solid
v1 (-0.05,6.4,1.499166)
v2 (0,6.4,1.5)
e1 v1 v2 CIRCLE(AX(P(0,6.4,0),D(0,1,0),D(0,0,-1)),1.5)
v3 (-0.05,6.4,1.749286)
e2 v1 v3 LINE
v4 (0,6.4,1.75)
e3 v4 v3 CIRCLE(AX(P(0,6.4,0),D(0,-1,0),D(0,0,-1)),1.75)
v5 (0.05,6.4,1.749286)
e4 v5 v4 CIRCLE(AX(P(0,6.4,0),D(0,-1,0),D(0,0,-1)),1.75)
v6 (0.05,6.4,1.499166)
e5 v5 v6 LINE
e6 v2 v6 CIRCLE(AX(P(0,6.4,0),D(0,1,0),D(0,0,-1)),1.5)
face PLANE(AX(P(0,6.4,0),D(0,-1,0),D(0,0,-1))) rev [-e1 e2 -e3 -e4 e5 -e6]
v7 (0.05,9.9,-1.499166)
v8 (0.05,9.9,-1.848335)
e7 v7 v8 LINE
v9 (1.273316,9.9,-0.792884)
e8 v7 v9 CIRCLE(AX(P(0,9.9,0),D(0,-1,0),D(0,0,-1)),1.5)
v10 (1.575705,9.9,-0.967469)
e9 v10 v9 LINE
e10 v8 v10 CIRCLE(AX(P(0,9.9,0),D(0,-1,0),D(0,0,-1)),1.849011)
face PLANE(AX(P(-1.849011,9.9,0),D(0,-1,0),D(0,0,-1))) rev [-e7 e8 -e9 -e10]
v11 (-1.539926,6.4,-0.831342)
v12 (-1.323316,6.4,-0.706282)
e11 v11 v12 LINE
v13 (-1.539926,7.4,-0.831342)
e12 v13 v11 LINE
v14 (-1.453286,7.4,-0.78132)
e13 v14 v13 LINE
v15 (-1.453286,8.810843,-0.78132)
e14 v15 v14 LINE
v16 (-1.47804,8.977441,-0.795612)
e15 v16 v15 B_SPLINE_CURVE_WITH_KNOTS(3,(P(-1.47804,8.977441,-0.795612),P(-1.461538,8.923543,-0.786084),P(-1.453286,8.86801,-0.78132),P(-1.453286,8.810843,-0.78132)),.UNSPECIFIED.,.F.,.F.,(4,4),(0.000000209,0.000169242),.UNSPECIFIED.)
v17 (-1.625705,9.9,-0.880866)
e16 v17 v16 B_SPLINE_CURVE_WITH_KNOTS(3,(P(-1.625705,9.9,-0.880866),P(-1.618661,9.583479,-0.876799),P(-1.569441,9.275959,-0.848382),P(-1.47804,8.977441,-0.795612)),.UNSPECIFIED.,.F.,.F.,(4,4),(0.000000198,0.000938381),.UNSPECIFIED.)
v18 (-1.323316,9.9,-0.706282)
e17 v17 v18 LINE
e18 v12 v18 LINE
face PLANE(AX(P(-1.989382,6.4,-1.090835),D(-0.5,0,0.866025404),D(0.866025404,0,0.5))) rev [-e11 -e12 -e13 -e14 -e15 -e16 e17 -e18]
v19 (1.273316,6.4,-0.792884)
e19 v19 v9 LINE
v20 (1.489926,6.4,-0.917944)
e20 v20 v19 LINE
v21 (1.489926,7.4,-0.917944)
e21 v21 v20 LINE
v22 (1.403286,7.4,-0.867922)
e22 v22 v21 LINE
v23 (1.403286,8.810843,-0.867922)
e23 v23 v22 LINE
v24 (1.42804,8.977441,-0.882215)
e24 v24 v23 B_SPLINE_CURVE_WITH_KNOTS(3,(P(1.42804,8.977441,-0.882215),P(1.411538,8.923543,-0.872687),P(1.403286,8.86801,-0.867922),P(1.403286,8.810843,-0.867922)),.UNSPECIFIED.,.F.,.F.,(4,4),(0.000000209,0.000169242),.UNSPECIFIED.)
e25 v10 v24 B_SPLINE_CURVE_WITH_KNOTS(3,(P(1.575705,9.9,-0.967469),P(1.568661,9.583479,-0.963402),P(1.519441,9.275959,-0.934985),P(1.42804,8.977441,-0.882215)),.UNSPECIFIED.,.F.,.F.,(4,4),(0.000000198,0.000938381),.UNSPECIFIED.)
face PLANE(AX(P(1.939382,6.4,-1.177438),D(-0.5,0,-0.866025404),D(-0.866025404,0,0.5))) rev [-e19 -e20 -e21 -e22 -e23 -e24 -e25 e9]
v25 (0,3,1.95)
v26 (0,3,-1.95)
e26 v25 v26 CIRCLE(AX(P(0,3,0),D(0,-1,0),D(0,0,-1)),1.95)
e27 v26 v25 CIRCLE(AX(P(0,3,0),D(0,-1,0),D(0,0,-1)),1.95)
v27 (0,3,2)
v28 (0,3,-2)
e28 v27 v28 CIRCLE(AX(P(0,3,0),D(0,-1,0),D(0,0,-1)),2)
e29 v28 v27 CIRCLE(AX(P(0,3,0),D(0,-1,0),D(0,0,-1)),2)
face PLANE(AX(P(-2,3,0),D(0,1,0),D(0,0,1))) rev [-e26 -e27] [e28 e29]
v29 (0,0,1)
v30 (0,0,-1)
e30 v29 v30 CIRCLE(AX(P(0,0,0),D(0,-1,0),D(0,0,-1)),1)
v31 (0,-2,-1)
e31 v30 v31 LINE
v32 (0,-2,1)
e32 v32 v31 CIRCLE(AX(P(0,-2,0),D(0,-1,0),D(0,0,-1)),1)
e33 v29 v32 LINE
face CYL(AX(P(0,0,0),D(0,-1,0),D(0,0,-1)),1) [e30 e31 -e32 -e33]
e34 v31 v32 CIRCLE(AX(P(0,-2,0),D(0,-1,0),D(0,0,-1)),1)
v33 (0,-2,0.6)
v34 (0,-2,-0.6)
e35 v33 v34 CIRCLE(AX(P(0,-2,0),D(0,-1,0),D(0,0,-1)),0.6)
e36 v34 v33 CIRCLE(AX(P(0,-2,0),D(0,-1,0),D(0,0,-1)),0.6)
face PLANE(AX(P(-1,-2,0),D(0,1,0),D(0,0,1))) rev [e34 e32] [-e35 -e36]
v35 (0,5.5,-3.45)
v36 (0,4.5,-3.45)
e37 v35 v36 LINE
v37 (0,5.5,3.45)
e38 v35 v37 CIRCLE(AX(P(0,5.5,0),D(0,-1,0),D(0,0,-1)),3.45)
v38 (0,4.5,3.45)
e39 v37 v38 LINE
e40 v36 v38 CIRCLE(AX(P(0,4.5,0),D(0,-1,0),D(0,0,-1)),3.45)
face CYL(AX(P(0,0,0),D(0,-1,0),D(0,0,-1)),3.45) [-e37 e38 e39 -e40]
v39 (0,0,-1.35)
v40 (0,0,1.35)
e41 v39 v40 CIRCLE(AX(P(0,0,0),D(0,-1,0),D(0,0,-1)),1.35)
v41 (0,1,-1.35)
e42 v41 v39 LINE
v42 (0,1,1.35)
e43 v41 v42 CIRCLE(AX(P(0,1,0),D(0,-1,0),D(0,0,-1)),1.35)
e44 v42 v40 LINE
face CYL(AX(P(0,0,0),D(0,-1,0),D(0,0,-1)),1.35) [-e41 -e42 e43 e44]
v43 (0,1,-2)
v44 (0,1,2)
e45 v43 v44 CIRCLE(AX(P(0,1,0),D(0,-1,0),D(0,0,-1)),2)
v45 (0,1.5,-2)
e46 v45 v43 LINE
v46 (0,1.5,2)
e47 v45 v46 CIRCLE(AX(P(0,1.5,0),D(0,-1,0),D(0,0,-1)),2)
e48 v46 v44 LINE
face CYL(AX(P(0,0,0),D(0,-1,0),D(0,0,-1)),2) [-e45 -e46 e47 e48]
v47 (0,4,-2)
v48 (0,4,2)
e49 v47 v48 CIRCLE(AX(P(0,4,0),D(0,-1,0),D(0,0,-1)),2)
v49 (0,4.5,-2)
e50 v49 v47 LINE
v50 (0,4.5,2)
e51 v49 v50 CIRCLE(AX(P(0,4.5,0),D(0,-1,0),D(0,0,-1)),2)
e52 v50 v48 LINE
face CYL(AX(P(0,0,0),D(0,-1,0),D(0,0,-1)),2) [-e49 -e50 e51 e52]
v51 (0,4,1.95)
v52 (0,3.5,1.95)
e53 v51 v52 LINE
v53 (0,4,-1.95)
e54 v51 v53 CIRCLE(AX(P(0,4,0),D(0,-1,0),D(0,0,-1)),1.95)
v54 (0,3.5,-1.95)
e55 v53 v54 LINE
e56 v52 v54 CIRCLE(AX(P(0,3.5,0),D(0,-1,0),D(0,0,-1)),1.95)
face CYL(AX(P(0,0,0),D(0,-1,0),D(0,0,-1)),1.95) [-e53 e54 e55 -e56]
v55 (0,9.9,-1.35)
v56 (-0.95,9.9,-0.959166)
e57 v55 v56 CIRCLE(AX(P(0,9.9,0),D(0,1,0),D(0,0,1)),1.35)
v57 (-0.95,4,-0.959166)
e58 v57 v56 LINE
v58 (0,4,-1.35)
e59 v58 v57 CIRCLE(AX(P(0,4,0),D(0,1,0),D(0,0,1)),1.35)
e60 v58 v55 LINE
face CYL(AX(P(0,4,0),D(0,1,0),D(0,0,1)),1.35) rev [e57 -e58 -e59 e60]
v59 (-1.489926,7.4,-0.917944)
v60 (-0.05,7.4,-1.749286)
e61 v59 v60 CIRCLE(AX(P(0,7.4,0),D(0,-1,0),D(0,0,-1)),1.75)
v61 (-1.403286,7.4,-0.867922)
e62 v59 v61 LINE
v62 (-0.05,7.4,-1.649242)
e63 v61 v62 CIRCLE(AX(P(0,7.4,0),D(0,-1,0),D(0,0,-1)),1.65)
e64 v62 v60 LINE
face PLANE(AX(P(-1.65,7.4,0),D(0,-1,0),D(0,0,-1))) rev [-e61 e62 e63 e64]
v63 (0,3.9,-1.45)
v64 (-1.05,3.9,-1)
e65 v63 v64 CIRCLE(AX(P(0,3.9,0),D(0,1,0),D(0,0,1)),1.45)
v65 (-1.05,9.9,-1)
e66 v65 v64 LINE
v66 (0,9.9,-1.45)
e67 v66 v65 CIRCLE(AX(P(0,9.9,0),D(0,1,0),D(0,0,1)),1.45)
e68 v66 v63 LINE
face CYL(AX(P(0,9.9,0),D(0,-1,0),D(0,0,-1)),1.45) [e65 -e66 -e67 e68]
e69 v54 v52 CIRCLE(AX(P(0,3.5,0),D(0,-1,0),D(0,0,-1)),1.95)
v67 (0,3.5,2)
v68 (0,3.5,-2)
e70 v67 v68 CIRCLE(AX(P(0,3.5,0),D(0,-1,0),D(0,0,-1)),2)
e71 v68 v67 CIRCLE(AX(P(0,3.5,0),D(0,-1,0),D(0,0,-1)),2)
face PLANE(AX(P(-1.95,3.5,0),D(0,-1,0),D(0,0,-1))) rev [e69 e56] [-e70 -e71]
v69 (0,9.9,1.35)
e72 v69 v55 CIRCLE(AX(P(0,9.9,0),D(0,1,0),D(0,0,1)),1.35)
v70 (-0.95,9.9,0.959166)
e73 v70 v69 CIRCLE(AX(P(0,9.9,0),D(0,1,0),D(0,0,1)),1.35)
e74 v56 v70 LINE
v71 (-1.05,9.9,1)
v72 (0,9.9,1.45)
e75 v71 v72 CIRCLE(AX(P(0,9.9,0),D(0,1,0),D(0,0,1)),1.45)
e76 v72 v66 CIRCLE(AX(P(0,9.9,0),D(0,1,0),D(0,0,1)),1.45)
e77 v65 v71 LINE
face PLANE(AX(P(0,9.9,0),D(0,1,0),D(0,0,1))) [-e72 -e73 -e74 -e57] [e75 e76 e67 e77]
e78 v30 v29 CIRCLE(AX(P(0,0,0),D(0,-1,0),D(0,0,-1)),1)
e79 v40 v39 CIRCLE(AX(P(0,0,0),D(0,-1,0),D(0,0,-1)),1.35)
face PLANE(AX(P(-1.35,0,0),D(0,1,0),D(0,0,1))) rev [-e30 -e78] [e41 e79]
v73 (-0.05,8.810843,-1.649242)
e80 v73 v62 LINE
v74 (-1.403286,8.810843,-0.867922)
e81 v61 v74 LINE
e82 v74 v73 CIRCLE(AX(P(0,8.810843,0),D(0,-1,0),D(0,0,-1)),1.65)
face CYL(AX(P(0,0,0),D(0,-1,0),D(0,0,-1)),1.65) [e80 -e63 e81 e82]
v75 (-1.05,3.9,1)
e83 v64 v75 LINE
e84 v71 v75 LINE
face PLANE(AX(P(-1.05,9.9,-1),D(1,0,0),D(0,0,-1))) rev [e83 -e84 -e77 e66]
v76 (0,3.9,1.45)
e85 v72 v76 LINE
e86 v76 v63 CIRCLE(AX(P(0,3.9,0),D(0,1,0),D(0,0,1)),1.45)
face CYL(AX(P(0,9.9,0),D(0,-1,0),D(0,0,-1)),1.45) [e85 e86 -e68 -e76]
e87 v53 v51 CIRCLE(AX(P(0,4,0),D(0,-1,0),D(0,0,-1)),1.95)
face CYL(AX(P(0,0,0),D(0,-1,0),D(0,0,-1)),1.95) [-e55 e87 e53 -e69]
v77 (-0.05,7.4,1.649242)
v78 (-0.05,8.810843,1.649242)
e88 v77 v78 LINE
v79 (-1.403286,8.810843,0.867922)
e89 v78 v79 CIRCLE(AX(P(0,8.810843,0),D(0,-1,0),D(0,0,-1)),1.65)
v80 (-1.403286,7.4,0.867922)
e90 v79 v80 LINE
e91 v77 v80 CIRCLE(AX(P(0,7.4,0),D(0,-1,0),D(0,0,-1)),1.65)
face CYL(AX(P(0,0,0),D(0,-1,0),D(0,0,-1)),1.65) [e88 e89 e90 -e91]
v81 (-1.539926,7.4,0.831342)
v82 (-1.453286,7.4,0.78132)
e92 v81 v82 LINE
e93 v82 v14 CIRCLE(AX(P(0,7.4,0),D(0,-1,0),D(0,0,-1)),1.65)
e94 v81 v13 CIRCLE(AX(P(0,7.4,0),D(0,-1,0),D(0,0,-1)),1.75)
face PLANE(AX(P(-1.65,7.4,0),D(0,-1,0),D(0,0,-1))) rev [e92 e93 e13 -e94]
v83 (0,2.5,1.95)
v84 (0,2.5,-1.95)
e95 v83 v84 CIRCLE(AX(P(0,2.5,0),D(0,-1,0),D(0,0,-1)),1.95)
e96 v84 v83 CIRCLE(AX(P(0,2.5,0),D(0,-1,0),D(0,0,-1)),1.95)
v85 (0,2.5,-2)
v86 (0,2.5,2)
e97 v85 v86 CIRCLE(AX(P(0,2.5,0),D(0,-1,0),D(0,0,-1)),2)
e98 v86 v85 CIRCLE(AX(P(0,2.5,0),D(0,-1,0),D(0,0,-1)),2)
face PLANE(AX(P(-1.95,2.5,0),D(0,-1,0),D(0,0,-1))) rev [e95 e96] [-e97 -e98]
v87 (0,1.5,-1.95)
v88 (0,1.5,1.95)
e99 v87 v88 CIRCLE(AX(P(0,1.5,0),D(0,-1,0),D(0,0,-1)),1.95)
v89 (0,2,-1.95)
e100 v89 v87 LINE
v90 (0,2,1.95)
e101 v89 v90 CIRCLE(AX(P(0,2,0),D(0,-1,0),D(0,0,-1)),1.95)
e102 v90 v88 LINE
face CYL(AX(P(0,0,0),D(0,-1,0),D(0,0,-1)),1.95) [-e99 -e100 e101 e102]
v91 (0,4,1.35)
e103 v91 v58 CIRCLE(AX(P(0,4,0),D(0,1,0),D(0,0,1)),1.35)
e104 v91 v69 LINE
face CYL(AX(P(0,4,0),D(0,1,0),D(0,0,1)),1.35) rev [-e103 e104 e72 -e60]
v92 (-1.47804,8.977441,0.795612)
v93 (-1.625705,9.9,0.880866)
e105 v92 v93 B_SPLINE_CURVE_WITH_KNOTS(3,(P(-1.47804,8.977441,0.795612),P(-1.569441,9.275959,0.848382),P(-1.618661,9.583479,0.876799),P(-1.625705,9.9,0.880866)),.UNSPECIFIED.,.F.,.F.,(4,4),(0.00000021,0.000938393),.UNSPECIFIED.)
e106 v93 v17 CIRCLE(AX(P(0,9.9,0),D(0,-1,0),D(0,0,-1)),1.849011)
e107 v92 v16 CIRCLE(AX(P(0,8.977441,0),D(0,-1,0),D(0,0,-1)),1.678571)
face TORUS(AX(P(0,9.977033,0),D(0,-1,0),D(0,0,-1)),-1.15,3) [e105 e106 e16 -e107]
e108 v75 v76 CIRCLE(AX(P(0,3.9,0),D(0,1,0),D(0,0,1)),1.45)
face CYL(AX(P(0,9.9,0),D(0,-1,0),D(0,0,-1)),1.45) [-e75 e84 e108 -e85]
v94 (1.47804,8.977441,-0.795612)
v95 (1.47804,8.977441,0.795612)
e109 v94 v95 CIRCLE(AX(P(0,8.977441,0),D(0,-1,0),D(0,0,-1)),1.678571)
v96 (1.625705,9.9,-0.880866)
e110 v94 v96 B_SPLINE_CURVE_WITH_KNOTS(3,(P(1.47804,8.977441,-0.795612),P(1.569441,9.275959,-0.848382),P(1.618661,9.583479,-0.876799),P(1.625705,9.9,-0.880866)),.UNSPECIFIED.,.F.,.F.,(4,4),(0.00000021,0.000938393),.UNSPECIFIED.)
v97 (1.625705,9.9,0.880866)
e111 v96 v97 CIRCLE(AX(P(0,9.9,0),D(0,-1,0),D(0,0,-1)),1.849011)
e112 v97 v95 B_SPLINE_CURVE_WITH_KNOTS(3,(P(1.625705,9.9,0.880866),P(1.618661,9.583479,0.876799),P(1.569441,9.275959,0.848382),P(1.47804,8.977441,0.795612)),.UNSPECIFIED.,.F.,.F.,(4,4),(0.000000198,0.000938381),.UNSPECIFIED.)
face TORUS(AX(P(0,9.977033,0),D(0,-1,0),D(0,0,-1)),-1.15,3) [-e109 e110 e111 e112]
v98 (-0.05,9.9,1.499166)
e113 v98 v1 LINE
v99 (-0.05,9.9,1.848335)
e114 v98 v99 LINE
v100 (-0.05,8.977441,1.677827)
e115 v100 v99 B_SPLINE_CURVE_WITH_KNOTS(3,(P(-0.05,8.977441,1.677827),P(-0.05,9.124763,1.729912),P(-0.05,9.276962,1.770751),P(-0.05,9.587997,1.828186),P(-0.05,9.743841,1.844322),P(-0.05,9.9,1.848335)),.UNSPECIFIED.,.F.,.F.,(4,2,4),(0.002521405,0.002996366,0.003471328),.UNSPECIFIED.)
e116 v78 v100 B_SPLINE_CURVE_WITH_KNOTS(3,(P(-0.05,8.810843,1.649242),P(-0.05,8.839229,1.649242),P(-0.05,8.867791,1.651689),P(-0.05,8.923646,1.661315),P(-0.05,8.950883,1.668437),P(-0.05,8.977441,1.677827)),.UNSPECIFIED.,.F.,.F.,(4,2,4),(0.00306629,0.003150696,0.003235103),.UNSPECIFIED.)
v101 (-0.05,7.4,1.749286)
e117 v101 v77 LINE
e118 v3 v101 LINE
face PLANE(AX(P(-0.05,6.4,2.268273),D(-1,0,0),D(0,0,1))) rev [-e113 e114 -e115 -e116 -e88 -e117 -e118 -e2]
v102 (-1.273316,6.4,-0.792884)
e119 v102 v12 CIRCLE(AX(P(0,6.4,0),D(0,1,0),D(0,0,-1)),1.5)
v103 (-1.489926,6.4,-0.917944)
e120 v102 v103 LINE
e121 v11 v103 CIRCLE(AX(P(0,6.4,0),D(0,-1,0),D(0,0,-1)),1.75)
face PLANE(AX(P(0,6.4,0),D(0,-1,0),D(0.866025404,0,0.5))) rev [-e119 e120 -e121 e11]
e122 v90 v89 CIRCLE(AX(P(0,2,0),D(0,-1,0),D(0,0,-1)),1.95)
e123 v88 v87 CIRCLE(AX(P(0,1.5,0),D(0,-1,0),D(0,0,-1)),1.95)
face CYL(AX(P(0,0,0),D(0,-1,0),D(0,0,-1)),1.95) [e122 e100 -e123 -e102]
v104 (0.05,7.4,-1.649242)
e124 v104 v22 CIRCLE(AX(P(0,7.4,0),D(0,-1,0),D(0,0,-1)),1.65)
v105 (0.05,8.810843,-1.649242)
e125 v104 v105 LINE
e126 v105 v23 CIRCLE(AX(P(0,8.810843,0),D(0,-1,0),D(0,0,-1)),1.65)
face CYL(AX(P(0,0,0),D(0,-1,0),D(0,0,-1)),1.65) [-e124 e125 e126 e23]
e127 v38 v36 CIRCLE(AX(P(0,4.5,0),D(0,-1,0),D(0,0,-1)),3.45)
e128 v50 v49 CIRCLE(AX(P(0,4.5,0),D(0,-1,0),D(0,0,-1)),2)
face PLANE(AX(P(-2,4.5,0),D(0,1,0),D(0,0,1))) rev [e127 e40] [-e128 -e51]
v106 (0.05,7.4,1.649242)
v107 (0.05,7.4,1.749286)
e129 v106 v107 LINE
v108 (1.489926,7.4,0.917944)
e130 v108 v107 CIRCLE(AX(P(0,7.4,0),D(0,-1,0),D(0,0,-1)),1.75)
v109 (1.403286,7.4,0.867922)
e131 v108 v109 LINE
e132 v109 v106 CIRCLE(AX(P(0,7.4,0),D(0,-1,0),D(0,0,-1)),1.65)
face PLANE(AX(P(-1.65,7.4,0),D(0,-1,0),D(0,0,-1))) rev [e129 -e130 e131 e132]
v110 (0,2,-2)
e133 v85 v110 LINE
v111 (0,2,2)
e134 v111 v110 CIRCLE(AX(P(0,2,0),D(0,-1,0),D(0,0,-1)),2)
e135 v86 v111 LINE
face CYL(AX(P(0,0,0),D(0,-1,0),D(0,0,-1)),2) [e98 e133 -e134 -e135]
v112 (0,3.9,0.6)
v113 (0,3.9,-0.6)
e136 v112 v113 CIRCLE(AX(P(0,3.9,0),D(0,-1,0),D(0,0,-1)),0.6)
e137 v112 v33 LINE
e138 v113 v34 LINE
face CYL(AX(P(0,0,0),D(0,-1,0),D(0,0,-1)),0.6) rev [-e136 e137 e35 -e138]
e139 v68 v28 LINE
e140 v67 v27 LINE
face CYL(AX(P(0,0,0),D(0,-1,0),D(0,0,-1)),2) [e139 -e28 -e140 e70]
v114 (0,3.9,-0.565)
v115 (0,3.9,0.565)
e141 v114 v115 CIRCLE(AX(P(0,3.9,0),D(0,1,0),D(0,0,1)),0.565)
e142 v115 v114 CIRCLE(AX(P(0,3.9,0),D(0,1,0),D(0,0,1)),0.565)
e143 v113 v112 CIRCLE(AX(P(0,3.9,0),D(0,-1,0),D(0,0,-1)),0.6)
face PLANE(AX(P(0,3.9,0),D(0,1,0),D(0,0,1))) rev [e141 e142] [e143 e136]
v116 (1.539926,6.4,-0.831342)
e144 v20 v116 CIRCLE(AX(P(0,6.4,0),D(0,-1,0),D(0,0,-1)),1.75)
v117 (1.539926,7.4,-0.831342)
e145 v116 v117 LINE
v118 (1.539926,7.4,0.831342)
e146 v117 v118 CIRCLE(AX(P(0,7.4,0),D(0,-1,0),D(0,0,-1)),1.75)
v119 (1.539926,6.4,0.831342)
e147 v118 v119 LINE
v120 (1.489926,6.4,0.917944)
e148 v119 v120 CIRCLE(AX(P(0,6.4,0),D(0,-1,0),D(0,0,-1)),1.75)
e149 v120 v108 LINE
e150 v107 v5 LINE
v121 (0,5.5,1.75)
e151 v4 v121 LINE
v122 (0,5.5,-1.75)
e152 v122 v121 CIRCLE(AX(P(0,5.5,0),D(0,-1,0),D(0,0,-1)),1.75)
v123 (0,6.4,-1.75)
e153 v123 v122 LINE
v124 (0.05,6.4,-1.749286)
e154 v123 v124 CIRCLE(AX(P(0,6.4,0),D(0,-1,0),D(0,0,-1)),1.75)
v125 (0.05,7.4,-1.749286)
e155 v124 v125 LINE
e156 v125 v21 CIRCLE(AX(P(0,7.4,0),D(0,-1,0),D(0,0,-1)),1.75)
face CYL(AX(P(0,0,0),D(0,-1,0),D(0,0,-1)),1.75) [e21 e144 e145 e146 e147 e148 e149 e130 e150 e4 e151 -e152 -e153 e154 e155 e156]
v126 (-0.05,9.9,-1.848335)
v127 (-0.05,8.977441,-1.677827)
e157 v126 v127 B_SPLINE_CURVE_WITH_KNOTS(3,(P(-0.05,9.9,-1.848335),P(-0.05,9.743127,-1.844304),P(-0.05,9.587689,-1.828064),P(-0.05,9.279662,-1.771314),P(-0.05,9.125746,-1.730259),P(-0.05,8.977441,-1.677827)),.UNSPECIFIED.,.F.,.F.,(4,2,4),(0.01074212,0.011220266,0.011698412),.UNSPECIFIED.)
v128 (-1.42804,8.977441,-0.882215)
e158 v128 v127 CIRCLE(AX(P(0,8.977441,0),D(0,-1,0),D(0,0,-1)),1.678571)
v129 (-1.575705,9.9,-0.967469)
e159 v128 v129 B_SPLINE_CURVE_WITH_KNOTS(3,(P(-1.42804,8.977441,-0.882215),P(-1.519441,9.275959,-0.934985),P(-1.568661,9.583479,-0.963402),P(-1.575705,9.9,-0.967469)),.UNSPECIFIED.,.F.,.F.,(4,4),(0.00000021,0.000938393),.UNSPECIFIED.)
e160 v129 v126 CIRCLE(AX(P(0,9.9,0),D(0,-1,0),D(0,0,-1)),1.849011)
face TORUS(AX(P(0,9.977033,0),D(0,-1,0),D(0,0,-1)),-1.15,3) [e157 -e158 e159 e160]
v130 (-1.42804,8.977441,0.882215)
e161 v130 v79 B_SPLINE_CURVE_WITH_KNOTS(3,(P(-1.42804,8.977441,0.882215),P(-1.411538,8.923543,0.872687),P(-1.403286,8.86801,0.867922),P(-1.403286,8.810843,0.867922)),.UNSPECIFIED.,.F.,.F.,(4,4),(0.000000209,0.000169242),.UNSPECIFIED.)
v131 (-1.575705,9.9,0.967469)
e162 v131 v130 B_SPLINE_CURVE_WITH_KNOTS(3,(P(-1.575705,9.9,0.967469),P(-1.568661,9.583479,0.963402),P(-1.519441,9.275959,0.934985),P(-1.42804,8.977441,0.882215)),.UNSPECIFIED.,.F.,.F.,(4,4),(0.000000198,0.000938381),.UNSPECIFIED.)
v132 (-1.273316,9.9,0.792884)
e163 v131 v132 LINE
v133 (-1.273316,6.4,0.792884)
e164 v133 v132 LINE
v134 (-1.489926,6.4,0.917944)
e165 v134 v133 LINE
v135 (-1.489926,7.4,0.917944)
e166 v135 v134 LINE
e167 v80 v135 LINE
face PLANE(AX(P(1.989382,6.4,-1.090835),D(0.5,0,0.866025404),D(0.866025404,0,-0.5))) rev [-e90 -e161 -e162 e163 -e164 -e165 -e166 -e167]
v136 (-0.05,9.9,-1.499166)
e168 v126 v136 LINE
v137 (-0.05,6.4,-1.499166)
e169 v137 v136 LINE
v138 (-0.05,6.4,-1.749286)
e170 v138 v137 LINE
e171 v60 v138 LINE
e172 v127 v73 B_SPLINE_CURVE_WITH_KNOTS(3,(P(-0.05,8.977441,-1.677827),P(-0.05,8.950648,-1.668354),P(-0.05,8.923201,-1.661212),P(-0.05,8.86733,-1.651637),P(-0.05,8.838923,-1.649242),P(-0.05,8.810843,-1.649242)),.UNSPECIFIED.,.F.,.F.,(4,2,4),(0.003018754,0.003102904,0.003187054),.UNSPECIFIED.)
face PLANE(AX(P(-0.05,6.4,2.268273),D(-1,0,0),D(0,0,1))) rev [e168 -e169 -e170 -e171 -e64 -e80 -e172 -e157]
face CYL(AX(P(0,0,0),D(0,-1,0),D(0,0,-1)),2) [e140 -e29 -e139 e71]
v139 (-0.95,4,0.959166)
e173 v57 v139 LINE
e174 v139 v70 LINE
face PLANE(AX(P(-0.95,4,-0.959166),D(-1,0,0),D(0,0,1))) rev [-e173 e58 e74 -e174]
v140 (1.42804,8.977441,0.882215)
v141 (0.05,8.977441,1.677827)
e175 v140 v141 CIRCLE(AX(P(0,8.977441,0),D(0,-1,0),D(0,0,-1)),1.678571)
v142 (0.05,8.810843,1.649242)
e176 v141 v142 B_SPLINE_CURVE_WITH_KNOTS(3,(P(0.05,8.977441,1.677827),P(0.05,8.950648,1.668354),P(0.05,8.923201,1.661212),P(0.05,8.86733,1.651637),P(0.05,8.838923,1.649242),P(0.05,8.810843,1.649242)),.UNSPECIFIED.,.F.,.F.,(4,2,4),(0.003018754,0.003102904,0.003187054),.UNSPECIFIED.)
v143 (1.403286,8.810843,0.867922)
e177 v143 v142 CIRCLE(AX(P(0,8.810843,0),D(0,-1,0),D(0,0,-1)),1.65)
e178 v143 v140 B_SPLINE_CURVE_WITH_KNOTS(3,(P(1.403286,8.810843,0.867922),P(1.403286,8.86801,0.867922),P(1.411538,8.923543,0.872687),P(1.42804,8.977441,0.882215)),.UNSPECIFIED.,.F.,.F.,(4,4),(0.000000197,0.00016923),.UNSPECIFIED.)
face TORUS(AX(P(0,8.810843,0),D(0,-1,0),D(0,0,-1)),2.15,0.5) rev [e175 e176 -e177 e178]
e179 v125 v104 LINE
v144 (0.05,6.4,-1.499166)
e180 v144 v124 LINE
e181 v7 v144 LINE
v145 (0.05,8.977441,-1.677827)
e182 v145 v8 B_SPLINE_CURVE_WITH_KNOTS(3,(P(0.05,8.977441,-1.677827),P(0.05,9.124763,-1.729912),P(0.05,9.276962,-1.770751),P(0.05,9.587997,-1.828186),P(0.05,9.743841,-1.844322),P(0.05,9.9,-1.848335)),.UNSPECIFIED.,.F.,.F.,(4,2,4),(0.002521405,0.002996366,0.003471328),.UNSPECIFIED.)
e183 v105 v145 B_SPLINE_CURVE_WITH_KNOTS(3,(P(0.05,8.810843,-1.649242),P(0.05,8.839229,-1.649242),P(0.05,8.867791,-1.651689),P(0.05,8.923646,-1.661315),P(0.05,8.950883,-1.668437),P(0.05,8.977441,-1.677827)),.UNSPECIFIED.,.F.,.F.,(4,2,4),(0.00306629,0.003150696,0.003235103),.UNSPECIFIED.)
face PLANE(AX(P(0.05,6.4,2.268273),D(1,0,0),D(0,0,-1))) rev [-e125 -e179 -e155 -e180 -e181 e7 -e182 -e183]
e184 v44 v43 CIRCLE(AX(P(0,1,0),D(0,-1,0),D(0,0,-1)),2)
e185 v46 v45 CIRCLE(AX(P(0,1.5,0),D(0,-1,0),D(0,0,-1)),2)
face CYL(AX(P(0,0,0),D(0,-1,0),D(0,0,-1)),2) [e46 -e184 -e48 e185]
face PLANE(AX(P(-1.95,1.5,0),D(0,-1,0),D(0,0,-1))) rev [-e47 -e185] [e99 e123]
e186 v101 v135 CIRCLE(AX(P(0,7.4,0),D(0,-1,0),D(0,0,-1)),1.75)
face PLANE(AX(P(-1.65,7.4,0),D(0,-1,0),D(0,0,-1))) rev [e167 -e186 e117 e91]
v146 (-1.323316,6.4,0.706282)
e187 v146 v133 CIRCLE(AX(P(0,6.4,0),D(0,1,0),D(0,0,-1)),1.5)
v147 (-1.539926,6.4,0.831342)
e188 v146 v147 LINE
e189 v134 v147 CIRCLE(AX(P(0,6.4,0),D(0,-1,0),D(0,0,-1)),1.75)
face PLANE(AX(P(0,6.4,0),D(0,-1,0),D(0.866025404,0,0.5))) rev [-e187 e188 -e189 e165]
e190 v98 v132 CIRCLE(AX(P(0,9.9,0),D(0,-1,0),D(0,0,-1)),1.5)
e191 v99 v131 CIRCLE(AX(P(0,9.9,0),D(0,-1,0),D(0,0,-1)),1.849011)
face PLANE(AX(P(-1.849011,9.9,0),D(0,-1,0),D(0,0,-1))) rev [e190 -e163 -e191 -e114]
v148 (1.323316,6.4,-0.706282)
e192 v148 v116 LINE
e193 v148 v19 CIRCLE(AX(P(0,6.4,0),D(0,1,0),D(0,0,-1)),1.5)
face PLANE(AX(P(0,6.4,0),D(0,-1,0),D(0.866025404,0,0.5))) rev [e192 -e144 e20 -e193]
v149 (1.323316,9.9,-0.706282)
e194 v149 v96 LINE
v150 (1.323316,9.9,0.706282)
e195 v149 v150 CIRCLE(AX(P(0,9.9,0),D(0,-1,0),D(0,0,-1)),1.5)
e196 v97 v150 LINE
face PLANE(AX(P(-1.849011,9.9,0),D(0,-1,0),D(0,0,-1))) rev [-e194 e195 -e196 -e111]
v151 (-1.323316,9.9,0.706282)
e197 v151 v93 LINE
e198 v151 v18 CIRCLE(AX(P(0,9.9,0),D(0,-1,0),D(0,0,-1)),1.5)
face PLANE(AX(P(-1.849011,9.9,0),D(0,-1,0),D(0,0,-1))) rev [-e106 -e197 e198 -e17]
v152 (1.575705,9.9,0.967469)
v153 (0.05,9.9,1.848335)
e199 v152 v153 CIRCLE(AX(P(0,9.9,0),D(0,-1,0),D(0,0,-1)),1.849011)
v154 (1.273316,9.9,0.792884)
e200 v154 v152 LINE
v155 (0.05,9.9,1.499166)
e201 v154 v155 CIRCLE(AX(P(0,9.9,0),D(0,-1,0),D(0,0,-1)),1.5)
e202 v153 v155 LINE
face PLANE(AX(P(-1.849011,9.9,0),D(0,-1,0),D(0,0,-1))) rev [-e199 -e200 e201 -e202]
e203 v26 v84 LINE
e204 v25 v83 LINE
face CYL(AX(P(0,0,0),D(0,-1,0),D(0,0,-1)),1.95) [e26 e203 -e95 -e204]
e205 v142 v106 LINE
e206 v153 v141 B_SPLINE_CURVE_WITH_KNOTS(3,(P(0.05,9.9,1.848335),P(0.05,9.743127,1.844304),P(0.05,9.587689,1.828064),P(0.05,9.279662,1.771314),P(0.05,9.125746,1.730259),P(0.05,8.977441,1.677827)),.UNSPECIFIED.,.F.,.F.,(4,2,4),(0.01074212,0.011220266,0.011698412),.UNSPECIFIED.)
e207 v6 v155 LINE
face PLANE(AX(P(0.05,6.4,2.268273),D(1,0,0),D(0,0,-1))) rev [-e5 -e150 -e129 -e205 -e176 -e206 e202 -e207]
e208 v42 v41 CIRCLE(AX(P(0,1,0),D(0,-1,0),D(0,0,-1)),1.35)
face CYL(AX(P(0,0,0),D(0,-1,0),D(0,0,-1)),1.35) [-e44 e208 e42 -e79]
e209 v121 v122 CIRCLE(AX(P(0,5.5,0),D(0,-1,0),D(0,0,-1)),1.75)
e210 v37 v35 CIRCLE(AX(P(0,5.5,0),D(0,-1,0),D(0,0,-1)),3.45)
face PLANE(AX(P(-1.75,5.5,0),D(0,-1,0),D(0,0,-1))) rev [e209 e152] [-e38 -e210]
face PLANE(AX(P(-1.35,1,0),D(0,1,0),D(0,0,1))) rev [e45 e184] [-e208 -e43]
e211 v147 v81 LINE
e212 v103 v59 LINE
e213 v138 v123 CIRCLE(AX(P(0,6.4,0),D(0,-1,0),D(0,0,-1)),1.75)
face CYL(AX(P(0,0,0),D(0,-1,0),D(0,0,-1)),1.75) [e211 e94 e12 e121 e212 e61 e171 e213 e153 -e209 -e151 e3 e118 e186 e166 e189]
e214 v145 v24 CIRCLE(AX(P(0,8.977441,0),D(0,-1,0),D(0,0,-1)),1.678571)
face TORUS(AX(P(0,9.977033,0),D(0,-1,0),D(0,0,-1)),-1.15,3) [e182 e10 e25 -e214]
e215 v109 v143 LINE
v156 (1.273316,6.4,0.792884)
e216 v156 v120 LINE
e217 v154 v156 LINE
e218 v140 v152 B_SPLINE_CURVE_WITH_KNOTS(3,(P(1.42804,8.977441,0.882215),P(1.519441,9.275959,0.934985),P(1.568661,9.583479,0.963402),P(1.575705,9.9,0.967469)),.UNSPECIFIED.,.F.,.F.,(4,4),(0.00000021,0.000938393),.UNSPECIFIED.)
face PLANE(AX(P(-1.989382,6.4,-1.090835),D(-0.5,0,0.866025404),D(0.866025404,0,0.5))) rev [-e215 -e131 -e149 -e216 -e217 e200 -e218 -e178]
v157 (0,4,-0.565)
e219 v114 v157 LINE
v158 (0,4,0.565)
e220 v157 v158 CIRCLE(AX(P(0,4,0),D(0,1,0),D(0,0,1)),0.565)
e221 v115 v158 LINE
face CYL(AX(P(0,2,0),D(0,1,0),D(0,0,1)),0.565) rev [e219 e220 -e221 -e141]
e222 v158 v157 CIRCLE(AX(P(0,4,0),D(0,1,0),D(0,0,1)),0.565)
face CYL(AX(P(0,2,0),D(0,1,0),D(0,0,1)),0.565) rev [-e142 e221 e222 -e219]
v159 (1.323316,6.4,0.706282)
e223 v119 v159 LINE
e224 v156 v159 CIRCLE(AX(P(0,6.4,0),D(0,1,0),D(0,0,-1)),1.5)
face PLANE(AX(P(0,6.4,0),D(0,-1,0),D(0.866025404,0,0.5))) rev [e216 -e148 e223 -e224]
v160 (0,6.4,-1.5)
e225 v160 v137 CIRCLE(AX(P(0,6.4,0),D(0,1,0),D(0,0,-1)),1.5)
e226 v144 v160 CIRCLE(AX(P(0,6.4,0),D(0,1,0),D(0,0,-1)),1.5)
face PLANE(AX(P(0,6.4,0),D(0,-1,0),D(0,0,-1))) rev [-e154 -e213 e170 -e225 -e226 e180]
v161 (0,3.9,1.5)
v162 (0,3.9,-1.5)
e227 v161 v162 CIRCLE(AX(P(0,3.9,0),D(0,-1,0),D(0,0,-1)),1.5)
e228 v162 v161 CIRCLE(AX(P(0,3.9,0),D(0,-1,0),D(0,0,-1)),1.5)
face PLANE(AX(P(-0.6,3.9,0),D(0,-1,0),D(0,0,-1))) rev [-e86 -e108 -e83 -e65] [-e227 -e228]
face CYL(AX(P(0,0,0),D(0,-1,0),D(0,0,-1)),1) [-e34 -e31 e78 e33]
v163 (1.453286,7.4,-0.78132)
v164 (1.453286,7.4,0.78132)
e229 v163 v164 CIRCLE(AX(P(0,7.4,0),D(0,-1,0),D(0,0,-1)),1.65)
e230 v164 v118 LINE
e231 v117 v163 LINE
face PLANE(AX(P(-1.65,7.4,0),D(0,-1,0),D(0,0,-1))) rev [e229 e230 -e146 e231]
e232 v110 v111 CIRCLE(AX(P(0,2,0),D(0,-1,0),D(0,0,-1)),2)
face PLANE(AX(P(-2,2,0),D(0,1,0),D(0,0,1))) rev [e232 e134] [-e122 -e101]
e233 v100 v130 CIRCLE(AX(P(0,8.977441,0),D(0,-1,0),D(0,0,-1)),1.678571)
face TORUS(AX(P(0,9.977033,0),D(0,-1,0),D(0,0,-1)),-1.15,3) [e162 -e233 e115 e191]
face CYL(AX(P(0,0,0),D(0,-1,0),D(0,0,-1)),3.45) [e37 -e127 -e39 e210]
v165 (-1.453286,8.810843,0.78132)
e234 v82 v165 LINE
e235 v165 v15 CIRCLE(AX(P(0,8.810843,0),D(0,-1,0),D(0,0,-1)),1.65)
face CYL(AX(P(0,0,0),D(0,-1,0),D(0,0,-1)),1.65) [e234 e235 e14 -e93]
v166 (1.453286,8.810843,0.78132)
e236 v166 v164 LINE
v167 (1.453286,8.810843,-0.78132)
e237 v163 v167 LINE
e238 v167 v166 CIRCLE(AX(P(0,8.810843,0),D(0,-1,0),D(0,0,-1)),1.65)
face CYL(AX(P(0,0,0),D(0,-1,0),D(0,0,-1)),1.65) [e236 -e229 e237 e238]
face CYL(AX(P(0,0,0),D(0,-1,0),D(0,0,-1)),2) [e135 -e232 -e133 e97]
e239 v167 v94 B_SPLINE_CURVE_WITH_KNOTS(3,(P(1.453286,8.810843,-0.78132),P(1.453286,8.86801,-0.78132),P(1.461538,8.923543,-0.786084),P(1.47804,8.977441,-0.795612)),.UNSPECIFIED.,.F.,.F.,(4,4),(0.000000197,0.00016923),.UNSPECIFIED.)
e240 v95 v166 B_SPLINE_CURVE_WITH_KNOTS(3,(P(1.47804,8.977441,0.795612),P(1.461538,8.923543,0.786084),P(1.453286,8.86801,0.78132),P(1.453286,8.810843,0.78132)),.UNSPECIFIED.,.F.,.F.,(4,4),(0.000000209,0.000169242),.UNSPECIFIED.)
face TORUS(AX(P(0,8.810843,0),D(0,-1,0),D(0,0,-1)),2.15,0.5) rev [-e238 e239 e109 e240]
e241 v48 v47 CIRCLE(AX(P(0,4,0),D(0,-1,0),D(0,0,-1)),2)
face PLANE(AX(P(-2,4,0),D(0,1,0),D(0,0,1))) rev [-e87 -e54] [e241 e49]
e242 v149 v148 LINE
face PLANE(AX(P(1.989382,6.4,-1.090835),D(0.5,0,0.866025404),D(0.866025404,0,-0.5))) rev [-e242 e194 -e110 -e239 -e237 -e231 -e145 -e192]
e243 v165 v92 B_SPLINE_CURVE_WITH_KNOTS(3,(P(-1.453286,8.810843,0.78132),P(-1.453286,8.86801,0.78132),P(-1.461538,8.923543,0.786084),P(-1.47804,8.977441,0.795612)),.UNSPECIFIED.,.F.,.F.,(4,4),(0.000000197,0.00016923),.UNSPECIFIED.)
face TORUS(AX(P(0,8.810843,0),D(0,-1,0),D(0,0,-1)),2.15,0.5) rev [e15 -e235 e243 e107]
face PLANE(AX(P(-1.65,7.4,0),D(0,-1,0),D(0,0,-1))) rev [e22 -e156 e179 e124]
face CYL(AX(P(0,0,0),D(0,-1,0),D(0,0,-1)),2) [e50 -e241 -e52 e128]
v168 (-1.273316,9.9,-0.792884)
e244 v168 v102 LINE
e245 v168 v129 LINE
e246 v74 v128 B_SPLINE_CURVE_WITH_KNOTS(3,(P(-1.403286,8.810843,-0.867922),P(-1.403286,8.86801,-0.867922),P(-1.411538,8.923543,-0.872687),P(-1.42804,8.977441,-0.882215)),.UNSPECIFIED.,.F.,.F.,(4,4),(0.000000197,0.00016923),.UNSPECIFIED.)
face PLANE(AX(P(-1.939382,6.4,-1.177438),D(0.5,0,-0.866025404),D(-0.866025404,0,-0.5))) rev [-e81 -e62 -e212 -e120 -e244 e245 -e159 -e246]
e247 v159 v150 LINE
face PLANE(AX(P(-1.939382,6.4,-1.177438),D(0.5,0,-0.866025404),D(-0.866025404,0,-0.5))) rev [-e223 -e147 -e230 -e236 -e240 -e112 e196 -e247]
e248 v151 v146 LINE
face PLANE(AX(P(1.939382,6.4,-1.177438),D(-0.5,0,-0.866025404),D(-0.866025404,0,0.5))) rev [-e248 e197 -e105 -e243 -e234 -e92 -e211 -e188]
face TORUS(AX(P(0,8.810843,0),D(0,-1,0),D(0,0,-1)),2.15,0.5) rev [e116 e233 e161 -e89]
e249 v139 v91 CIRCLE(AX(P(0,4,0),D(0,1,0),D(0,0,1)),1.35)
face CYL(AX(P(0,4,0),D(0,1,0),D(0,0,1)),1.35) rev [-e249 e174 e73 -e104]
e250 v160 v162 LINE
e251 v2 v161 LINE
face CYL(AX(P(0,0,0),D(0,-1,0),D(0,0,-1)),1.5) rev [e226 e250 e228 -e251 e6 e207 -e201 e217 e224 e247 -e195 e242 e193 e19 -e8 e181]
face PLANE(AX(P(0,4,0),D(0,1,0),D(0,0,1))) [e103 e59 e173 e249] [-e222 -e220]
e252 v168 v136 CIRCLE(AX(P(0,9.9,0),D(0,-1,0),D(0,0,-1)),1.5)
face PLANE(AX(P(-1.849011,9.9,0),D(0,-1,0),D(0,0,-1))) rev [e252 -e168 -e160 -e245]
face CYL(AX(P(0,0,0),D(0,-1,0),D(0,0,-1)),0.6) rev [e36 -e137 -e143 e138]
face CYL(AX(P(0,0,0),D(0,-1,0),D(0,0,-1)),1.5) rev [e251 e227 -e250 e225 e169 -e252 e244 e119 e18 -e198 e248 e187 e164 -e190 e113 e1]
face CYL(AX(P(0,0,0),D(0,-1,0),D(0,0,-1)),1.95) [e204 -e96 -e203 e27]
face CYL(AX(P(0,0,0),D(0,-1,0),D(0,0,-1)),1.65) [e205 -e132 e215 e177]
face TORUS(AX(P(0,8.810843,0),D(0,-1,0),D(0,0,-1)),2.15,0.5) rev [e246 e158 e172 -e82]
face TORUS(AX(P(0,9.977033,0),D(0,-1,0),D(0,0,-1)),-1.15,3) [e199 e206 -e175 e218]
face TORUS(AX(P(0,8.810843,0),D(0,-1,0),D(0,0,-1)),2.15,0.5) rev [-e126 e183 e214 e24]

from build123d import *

# Parameters (mm, degrees)
SKETCH2_W           = 0.1
SKETCH2_H           = 4.53654667
CUT_EXTRUDE1_DEPTH  = 3.5
CIRPATTERN1_COUNT   = 3
BOSS_EXTRUDE1_DEPTH = 6
CUT_EXTRUDE2_DEPTH  = 5.9
SKETCH7_R           = 0.565
CUT_EXTRUDE3_DEPTH  = 2


with BuildPart() as part:
    # Sketch1 → Revolve1 (revolve)
    with BuildSketch(Plane.XY, mode=Mode.PRIVATE) as revolve1_sk:
        with BuildLine():
            Line((-1.35, 0), (-1.35, 1))
            Line((-1.35, 1), (-2, 1))
            Line((-2, 1), (-2, 1.5))
            Line((-2, 1.5), (-1.95, 1.5))
            Line((-1.95, 1.5), (-1.95, 2))
            Line((-1.95, 2), (-2, 2))
            Line((-2, 2), (-2, 2.5))
            Line((-2, 2.5), (-1.95, 2.5))
            Line((-1.95, 2.5), (-1.95, 3))
            Line((-1.95, 3), (-2, 3))
            Line((-2, 3), (-2, 3.5))
            Line((-2, 3.5), (-1.95, 3.5))
            Line((-1.95, 3.5), (-1.95, 4))
            Line((-1.95, 4), (-2, 4))
            Line((-2, 4), (-2, 4.5))
            Line((-2, 4.5), (-3.45, 4.5))
            Line((-3.45, 4.5), (-3.45, 5.5))
            Line((-3.45, 5.5), (-1.75, 5.5))
            Line((-1.75, 5.5), (-1.75, 7.4))
            Line((-1.75, 7.4), (-1.65, 7.4))
            Line((-1.65, 7.4), (-1.65, 8.810842582))
            ThreePointArc((-1.65, 8.810842582), (-1.65719462, 8.895358008), (-1.678571429, 8.977441208))
            ThreePointArc((-1.678571429, 8.977441208), (-1.800077526, 9.432016823), (-1.849010824, 9.9))
            Line((-1.849010824, 9.9), (-1.5, 9.9))
            Line((-1.5, 9.9), (-1.5, 3.9))
            Line((-1.5, 3.9), (-0.6, 3.9))
            Line((-0.6, 3.9), (-0.6, -2))
            Line((-0.6, -2), (-1, -2))
            Line((-1, -2), (-1, 0))
            Line((-1, 0), (-1.35, 0))
        make_face()
    revolve(revolve1_sk.sketch.rotate(Axis((0, 0, 0), (0, 1, 0)), 270), axis=Axis((0, 0, 0), (0, 1, 0)))

    # Sketch2 → Cut-Extrude1 (cut)
    with BuildSketch(Plane(origin=(0, 9.9, 0), x_dir=(1, 0, 0), z_dir=(0, 1, 0))):
        Rectangle(SKETCH2_W, SKETCH2_H)
    cut_extrude1 = extrude(amount=-CUT_EXTRUDE1_DEPTH, mode=Mode.SUBTRACT)

    # CirPattern1: Cut-Extrude1 ×3 about axis
    cirpattern1_axis = Axis((0, 0, 0), (0, 1, 0))
    for i in range(1, CIRPATTERN1_COUNT):
        add(cut_extrude1.rotate(cirpattern1_axis, i * 360 / CIRPATTERN1_COUNT), mode=Mode.SUBTRACT)

    # Sketch5 → Boss-Extrude1 (add)
    with BuildSketch(Plane(origin=(0, 3.9, 0), x_dir=(1, 0, 0), z_dir=(0, 1, 0))):
        with BuildLine():
            Line((-1.05, 1), (-1.05, -1))
            ThreePointArc((-1.05, -1), (1.45, 0), (-1.05, 1))
        make_face()
    extrude(amount=BOSS_EXTRUDE1_DEPTH)

    # Sketch6 → Cut-Extrude2 (cut)
    with BuildSketch(Plane(origin=(0, 9.9, 0), x_dir=(1, 0, 0), z_dir=(0, 1, 0))):
        with BuildLine():
            Line((-0.95, 0.959166305), (-0.95, -0.959166305))
            ThreePointArc((-0.95, -0.959166305), (1.35, 0), (-0.95, 0.959166305))
        make_face()
    extrude(amount=-CUT_EXTRUDE2_DEPTH, mode=Mode.SUBTRACT)

    # Sketch7 → Cut-Extrude3 (cut)
    with BuildSketch(Plane(origin=(0, 4, 0), x_dir=(1, 0, 0), z_dir=(0, 1, 0))):
        with Locations(Location((0, 0, 0), (0, 0, 270))):
            Circle(SKETCH7_R)
    extrude(amount=-CUT_EXTRUDE3_DEPTH, mode=Mode.SUBTRACT)


solid = part.part
